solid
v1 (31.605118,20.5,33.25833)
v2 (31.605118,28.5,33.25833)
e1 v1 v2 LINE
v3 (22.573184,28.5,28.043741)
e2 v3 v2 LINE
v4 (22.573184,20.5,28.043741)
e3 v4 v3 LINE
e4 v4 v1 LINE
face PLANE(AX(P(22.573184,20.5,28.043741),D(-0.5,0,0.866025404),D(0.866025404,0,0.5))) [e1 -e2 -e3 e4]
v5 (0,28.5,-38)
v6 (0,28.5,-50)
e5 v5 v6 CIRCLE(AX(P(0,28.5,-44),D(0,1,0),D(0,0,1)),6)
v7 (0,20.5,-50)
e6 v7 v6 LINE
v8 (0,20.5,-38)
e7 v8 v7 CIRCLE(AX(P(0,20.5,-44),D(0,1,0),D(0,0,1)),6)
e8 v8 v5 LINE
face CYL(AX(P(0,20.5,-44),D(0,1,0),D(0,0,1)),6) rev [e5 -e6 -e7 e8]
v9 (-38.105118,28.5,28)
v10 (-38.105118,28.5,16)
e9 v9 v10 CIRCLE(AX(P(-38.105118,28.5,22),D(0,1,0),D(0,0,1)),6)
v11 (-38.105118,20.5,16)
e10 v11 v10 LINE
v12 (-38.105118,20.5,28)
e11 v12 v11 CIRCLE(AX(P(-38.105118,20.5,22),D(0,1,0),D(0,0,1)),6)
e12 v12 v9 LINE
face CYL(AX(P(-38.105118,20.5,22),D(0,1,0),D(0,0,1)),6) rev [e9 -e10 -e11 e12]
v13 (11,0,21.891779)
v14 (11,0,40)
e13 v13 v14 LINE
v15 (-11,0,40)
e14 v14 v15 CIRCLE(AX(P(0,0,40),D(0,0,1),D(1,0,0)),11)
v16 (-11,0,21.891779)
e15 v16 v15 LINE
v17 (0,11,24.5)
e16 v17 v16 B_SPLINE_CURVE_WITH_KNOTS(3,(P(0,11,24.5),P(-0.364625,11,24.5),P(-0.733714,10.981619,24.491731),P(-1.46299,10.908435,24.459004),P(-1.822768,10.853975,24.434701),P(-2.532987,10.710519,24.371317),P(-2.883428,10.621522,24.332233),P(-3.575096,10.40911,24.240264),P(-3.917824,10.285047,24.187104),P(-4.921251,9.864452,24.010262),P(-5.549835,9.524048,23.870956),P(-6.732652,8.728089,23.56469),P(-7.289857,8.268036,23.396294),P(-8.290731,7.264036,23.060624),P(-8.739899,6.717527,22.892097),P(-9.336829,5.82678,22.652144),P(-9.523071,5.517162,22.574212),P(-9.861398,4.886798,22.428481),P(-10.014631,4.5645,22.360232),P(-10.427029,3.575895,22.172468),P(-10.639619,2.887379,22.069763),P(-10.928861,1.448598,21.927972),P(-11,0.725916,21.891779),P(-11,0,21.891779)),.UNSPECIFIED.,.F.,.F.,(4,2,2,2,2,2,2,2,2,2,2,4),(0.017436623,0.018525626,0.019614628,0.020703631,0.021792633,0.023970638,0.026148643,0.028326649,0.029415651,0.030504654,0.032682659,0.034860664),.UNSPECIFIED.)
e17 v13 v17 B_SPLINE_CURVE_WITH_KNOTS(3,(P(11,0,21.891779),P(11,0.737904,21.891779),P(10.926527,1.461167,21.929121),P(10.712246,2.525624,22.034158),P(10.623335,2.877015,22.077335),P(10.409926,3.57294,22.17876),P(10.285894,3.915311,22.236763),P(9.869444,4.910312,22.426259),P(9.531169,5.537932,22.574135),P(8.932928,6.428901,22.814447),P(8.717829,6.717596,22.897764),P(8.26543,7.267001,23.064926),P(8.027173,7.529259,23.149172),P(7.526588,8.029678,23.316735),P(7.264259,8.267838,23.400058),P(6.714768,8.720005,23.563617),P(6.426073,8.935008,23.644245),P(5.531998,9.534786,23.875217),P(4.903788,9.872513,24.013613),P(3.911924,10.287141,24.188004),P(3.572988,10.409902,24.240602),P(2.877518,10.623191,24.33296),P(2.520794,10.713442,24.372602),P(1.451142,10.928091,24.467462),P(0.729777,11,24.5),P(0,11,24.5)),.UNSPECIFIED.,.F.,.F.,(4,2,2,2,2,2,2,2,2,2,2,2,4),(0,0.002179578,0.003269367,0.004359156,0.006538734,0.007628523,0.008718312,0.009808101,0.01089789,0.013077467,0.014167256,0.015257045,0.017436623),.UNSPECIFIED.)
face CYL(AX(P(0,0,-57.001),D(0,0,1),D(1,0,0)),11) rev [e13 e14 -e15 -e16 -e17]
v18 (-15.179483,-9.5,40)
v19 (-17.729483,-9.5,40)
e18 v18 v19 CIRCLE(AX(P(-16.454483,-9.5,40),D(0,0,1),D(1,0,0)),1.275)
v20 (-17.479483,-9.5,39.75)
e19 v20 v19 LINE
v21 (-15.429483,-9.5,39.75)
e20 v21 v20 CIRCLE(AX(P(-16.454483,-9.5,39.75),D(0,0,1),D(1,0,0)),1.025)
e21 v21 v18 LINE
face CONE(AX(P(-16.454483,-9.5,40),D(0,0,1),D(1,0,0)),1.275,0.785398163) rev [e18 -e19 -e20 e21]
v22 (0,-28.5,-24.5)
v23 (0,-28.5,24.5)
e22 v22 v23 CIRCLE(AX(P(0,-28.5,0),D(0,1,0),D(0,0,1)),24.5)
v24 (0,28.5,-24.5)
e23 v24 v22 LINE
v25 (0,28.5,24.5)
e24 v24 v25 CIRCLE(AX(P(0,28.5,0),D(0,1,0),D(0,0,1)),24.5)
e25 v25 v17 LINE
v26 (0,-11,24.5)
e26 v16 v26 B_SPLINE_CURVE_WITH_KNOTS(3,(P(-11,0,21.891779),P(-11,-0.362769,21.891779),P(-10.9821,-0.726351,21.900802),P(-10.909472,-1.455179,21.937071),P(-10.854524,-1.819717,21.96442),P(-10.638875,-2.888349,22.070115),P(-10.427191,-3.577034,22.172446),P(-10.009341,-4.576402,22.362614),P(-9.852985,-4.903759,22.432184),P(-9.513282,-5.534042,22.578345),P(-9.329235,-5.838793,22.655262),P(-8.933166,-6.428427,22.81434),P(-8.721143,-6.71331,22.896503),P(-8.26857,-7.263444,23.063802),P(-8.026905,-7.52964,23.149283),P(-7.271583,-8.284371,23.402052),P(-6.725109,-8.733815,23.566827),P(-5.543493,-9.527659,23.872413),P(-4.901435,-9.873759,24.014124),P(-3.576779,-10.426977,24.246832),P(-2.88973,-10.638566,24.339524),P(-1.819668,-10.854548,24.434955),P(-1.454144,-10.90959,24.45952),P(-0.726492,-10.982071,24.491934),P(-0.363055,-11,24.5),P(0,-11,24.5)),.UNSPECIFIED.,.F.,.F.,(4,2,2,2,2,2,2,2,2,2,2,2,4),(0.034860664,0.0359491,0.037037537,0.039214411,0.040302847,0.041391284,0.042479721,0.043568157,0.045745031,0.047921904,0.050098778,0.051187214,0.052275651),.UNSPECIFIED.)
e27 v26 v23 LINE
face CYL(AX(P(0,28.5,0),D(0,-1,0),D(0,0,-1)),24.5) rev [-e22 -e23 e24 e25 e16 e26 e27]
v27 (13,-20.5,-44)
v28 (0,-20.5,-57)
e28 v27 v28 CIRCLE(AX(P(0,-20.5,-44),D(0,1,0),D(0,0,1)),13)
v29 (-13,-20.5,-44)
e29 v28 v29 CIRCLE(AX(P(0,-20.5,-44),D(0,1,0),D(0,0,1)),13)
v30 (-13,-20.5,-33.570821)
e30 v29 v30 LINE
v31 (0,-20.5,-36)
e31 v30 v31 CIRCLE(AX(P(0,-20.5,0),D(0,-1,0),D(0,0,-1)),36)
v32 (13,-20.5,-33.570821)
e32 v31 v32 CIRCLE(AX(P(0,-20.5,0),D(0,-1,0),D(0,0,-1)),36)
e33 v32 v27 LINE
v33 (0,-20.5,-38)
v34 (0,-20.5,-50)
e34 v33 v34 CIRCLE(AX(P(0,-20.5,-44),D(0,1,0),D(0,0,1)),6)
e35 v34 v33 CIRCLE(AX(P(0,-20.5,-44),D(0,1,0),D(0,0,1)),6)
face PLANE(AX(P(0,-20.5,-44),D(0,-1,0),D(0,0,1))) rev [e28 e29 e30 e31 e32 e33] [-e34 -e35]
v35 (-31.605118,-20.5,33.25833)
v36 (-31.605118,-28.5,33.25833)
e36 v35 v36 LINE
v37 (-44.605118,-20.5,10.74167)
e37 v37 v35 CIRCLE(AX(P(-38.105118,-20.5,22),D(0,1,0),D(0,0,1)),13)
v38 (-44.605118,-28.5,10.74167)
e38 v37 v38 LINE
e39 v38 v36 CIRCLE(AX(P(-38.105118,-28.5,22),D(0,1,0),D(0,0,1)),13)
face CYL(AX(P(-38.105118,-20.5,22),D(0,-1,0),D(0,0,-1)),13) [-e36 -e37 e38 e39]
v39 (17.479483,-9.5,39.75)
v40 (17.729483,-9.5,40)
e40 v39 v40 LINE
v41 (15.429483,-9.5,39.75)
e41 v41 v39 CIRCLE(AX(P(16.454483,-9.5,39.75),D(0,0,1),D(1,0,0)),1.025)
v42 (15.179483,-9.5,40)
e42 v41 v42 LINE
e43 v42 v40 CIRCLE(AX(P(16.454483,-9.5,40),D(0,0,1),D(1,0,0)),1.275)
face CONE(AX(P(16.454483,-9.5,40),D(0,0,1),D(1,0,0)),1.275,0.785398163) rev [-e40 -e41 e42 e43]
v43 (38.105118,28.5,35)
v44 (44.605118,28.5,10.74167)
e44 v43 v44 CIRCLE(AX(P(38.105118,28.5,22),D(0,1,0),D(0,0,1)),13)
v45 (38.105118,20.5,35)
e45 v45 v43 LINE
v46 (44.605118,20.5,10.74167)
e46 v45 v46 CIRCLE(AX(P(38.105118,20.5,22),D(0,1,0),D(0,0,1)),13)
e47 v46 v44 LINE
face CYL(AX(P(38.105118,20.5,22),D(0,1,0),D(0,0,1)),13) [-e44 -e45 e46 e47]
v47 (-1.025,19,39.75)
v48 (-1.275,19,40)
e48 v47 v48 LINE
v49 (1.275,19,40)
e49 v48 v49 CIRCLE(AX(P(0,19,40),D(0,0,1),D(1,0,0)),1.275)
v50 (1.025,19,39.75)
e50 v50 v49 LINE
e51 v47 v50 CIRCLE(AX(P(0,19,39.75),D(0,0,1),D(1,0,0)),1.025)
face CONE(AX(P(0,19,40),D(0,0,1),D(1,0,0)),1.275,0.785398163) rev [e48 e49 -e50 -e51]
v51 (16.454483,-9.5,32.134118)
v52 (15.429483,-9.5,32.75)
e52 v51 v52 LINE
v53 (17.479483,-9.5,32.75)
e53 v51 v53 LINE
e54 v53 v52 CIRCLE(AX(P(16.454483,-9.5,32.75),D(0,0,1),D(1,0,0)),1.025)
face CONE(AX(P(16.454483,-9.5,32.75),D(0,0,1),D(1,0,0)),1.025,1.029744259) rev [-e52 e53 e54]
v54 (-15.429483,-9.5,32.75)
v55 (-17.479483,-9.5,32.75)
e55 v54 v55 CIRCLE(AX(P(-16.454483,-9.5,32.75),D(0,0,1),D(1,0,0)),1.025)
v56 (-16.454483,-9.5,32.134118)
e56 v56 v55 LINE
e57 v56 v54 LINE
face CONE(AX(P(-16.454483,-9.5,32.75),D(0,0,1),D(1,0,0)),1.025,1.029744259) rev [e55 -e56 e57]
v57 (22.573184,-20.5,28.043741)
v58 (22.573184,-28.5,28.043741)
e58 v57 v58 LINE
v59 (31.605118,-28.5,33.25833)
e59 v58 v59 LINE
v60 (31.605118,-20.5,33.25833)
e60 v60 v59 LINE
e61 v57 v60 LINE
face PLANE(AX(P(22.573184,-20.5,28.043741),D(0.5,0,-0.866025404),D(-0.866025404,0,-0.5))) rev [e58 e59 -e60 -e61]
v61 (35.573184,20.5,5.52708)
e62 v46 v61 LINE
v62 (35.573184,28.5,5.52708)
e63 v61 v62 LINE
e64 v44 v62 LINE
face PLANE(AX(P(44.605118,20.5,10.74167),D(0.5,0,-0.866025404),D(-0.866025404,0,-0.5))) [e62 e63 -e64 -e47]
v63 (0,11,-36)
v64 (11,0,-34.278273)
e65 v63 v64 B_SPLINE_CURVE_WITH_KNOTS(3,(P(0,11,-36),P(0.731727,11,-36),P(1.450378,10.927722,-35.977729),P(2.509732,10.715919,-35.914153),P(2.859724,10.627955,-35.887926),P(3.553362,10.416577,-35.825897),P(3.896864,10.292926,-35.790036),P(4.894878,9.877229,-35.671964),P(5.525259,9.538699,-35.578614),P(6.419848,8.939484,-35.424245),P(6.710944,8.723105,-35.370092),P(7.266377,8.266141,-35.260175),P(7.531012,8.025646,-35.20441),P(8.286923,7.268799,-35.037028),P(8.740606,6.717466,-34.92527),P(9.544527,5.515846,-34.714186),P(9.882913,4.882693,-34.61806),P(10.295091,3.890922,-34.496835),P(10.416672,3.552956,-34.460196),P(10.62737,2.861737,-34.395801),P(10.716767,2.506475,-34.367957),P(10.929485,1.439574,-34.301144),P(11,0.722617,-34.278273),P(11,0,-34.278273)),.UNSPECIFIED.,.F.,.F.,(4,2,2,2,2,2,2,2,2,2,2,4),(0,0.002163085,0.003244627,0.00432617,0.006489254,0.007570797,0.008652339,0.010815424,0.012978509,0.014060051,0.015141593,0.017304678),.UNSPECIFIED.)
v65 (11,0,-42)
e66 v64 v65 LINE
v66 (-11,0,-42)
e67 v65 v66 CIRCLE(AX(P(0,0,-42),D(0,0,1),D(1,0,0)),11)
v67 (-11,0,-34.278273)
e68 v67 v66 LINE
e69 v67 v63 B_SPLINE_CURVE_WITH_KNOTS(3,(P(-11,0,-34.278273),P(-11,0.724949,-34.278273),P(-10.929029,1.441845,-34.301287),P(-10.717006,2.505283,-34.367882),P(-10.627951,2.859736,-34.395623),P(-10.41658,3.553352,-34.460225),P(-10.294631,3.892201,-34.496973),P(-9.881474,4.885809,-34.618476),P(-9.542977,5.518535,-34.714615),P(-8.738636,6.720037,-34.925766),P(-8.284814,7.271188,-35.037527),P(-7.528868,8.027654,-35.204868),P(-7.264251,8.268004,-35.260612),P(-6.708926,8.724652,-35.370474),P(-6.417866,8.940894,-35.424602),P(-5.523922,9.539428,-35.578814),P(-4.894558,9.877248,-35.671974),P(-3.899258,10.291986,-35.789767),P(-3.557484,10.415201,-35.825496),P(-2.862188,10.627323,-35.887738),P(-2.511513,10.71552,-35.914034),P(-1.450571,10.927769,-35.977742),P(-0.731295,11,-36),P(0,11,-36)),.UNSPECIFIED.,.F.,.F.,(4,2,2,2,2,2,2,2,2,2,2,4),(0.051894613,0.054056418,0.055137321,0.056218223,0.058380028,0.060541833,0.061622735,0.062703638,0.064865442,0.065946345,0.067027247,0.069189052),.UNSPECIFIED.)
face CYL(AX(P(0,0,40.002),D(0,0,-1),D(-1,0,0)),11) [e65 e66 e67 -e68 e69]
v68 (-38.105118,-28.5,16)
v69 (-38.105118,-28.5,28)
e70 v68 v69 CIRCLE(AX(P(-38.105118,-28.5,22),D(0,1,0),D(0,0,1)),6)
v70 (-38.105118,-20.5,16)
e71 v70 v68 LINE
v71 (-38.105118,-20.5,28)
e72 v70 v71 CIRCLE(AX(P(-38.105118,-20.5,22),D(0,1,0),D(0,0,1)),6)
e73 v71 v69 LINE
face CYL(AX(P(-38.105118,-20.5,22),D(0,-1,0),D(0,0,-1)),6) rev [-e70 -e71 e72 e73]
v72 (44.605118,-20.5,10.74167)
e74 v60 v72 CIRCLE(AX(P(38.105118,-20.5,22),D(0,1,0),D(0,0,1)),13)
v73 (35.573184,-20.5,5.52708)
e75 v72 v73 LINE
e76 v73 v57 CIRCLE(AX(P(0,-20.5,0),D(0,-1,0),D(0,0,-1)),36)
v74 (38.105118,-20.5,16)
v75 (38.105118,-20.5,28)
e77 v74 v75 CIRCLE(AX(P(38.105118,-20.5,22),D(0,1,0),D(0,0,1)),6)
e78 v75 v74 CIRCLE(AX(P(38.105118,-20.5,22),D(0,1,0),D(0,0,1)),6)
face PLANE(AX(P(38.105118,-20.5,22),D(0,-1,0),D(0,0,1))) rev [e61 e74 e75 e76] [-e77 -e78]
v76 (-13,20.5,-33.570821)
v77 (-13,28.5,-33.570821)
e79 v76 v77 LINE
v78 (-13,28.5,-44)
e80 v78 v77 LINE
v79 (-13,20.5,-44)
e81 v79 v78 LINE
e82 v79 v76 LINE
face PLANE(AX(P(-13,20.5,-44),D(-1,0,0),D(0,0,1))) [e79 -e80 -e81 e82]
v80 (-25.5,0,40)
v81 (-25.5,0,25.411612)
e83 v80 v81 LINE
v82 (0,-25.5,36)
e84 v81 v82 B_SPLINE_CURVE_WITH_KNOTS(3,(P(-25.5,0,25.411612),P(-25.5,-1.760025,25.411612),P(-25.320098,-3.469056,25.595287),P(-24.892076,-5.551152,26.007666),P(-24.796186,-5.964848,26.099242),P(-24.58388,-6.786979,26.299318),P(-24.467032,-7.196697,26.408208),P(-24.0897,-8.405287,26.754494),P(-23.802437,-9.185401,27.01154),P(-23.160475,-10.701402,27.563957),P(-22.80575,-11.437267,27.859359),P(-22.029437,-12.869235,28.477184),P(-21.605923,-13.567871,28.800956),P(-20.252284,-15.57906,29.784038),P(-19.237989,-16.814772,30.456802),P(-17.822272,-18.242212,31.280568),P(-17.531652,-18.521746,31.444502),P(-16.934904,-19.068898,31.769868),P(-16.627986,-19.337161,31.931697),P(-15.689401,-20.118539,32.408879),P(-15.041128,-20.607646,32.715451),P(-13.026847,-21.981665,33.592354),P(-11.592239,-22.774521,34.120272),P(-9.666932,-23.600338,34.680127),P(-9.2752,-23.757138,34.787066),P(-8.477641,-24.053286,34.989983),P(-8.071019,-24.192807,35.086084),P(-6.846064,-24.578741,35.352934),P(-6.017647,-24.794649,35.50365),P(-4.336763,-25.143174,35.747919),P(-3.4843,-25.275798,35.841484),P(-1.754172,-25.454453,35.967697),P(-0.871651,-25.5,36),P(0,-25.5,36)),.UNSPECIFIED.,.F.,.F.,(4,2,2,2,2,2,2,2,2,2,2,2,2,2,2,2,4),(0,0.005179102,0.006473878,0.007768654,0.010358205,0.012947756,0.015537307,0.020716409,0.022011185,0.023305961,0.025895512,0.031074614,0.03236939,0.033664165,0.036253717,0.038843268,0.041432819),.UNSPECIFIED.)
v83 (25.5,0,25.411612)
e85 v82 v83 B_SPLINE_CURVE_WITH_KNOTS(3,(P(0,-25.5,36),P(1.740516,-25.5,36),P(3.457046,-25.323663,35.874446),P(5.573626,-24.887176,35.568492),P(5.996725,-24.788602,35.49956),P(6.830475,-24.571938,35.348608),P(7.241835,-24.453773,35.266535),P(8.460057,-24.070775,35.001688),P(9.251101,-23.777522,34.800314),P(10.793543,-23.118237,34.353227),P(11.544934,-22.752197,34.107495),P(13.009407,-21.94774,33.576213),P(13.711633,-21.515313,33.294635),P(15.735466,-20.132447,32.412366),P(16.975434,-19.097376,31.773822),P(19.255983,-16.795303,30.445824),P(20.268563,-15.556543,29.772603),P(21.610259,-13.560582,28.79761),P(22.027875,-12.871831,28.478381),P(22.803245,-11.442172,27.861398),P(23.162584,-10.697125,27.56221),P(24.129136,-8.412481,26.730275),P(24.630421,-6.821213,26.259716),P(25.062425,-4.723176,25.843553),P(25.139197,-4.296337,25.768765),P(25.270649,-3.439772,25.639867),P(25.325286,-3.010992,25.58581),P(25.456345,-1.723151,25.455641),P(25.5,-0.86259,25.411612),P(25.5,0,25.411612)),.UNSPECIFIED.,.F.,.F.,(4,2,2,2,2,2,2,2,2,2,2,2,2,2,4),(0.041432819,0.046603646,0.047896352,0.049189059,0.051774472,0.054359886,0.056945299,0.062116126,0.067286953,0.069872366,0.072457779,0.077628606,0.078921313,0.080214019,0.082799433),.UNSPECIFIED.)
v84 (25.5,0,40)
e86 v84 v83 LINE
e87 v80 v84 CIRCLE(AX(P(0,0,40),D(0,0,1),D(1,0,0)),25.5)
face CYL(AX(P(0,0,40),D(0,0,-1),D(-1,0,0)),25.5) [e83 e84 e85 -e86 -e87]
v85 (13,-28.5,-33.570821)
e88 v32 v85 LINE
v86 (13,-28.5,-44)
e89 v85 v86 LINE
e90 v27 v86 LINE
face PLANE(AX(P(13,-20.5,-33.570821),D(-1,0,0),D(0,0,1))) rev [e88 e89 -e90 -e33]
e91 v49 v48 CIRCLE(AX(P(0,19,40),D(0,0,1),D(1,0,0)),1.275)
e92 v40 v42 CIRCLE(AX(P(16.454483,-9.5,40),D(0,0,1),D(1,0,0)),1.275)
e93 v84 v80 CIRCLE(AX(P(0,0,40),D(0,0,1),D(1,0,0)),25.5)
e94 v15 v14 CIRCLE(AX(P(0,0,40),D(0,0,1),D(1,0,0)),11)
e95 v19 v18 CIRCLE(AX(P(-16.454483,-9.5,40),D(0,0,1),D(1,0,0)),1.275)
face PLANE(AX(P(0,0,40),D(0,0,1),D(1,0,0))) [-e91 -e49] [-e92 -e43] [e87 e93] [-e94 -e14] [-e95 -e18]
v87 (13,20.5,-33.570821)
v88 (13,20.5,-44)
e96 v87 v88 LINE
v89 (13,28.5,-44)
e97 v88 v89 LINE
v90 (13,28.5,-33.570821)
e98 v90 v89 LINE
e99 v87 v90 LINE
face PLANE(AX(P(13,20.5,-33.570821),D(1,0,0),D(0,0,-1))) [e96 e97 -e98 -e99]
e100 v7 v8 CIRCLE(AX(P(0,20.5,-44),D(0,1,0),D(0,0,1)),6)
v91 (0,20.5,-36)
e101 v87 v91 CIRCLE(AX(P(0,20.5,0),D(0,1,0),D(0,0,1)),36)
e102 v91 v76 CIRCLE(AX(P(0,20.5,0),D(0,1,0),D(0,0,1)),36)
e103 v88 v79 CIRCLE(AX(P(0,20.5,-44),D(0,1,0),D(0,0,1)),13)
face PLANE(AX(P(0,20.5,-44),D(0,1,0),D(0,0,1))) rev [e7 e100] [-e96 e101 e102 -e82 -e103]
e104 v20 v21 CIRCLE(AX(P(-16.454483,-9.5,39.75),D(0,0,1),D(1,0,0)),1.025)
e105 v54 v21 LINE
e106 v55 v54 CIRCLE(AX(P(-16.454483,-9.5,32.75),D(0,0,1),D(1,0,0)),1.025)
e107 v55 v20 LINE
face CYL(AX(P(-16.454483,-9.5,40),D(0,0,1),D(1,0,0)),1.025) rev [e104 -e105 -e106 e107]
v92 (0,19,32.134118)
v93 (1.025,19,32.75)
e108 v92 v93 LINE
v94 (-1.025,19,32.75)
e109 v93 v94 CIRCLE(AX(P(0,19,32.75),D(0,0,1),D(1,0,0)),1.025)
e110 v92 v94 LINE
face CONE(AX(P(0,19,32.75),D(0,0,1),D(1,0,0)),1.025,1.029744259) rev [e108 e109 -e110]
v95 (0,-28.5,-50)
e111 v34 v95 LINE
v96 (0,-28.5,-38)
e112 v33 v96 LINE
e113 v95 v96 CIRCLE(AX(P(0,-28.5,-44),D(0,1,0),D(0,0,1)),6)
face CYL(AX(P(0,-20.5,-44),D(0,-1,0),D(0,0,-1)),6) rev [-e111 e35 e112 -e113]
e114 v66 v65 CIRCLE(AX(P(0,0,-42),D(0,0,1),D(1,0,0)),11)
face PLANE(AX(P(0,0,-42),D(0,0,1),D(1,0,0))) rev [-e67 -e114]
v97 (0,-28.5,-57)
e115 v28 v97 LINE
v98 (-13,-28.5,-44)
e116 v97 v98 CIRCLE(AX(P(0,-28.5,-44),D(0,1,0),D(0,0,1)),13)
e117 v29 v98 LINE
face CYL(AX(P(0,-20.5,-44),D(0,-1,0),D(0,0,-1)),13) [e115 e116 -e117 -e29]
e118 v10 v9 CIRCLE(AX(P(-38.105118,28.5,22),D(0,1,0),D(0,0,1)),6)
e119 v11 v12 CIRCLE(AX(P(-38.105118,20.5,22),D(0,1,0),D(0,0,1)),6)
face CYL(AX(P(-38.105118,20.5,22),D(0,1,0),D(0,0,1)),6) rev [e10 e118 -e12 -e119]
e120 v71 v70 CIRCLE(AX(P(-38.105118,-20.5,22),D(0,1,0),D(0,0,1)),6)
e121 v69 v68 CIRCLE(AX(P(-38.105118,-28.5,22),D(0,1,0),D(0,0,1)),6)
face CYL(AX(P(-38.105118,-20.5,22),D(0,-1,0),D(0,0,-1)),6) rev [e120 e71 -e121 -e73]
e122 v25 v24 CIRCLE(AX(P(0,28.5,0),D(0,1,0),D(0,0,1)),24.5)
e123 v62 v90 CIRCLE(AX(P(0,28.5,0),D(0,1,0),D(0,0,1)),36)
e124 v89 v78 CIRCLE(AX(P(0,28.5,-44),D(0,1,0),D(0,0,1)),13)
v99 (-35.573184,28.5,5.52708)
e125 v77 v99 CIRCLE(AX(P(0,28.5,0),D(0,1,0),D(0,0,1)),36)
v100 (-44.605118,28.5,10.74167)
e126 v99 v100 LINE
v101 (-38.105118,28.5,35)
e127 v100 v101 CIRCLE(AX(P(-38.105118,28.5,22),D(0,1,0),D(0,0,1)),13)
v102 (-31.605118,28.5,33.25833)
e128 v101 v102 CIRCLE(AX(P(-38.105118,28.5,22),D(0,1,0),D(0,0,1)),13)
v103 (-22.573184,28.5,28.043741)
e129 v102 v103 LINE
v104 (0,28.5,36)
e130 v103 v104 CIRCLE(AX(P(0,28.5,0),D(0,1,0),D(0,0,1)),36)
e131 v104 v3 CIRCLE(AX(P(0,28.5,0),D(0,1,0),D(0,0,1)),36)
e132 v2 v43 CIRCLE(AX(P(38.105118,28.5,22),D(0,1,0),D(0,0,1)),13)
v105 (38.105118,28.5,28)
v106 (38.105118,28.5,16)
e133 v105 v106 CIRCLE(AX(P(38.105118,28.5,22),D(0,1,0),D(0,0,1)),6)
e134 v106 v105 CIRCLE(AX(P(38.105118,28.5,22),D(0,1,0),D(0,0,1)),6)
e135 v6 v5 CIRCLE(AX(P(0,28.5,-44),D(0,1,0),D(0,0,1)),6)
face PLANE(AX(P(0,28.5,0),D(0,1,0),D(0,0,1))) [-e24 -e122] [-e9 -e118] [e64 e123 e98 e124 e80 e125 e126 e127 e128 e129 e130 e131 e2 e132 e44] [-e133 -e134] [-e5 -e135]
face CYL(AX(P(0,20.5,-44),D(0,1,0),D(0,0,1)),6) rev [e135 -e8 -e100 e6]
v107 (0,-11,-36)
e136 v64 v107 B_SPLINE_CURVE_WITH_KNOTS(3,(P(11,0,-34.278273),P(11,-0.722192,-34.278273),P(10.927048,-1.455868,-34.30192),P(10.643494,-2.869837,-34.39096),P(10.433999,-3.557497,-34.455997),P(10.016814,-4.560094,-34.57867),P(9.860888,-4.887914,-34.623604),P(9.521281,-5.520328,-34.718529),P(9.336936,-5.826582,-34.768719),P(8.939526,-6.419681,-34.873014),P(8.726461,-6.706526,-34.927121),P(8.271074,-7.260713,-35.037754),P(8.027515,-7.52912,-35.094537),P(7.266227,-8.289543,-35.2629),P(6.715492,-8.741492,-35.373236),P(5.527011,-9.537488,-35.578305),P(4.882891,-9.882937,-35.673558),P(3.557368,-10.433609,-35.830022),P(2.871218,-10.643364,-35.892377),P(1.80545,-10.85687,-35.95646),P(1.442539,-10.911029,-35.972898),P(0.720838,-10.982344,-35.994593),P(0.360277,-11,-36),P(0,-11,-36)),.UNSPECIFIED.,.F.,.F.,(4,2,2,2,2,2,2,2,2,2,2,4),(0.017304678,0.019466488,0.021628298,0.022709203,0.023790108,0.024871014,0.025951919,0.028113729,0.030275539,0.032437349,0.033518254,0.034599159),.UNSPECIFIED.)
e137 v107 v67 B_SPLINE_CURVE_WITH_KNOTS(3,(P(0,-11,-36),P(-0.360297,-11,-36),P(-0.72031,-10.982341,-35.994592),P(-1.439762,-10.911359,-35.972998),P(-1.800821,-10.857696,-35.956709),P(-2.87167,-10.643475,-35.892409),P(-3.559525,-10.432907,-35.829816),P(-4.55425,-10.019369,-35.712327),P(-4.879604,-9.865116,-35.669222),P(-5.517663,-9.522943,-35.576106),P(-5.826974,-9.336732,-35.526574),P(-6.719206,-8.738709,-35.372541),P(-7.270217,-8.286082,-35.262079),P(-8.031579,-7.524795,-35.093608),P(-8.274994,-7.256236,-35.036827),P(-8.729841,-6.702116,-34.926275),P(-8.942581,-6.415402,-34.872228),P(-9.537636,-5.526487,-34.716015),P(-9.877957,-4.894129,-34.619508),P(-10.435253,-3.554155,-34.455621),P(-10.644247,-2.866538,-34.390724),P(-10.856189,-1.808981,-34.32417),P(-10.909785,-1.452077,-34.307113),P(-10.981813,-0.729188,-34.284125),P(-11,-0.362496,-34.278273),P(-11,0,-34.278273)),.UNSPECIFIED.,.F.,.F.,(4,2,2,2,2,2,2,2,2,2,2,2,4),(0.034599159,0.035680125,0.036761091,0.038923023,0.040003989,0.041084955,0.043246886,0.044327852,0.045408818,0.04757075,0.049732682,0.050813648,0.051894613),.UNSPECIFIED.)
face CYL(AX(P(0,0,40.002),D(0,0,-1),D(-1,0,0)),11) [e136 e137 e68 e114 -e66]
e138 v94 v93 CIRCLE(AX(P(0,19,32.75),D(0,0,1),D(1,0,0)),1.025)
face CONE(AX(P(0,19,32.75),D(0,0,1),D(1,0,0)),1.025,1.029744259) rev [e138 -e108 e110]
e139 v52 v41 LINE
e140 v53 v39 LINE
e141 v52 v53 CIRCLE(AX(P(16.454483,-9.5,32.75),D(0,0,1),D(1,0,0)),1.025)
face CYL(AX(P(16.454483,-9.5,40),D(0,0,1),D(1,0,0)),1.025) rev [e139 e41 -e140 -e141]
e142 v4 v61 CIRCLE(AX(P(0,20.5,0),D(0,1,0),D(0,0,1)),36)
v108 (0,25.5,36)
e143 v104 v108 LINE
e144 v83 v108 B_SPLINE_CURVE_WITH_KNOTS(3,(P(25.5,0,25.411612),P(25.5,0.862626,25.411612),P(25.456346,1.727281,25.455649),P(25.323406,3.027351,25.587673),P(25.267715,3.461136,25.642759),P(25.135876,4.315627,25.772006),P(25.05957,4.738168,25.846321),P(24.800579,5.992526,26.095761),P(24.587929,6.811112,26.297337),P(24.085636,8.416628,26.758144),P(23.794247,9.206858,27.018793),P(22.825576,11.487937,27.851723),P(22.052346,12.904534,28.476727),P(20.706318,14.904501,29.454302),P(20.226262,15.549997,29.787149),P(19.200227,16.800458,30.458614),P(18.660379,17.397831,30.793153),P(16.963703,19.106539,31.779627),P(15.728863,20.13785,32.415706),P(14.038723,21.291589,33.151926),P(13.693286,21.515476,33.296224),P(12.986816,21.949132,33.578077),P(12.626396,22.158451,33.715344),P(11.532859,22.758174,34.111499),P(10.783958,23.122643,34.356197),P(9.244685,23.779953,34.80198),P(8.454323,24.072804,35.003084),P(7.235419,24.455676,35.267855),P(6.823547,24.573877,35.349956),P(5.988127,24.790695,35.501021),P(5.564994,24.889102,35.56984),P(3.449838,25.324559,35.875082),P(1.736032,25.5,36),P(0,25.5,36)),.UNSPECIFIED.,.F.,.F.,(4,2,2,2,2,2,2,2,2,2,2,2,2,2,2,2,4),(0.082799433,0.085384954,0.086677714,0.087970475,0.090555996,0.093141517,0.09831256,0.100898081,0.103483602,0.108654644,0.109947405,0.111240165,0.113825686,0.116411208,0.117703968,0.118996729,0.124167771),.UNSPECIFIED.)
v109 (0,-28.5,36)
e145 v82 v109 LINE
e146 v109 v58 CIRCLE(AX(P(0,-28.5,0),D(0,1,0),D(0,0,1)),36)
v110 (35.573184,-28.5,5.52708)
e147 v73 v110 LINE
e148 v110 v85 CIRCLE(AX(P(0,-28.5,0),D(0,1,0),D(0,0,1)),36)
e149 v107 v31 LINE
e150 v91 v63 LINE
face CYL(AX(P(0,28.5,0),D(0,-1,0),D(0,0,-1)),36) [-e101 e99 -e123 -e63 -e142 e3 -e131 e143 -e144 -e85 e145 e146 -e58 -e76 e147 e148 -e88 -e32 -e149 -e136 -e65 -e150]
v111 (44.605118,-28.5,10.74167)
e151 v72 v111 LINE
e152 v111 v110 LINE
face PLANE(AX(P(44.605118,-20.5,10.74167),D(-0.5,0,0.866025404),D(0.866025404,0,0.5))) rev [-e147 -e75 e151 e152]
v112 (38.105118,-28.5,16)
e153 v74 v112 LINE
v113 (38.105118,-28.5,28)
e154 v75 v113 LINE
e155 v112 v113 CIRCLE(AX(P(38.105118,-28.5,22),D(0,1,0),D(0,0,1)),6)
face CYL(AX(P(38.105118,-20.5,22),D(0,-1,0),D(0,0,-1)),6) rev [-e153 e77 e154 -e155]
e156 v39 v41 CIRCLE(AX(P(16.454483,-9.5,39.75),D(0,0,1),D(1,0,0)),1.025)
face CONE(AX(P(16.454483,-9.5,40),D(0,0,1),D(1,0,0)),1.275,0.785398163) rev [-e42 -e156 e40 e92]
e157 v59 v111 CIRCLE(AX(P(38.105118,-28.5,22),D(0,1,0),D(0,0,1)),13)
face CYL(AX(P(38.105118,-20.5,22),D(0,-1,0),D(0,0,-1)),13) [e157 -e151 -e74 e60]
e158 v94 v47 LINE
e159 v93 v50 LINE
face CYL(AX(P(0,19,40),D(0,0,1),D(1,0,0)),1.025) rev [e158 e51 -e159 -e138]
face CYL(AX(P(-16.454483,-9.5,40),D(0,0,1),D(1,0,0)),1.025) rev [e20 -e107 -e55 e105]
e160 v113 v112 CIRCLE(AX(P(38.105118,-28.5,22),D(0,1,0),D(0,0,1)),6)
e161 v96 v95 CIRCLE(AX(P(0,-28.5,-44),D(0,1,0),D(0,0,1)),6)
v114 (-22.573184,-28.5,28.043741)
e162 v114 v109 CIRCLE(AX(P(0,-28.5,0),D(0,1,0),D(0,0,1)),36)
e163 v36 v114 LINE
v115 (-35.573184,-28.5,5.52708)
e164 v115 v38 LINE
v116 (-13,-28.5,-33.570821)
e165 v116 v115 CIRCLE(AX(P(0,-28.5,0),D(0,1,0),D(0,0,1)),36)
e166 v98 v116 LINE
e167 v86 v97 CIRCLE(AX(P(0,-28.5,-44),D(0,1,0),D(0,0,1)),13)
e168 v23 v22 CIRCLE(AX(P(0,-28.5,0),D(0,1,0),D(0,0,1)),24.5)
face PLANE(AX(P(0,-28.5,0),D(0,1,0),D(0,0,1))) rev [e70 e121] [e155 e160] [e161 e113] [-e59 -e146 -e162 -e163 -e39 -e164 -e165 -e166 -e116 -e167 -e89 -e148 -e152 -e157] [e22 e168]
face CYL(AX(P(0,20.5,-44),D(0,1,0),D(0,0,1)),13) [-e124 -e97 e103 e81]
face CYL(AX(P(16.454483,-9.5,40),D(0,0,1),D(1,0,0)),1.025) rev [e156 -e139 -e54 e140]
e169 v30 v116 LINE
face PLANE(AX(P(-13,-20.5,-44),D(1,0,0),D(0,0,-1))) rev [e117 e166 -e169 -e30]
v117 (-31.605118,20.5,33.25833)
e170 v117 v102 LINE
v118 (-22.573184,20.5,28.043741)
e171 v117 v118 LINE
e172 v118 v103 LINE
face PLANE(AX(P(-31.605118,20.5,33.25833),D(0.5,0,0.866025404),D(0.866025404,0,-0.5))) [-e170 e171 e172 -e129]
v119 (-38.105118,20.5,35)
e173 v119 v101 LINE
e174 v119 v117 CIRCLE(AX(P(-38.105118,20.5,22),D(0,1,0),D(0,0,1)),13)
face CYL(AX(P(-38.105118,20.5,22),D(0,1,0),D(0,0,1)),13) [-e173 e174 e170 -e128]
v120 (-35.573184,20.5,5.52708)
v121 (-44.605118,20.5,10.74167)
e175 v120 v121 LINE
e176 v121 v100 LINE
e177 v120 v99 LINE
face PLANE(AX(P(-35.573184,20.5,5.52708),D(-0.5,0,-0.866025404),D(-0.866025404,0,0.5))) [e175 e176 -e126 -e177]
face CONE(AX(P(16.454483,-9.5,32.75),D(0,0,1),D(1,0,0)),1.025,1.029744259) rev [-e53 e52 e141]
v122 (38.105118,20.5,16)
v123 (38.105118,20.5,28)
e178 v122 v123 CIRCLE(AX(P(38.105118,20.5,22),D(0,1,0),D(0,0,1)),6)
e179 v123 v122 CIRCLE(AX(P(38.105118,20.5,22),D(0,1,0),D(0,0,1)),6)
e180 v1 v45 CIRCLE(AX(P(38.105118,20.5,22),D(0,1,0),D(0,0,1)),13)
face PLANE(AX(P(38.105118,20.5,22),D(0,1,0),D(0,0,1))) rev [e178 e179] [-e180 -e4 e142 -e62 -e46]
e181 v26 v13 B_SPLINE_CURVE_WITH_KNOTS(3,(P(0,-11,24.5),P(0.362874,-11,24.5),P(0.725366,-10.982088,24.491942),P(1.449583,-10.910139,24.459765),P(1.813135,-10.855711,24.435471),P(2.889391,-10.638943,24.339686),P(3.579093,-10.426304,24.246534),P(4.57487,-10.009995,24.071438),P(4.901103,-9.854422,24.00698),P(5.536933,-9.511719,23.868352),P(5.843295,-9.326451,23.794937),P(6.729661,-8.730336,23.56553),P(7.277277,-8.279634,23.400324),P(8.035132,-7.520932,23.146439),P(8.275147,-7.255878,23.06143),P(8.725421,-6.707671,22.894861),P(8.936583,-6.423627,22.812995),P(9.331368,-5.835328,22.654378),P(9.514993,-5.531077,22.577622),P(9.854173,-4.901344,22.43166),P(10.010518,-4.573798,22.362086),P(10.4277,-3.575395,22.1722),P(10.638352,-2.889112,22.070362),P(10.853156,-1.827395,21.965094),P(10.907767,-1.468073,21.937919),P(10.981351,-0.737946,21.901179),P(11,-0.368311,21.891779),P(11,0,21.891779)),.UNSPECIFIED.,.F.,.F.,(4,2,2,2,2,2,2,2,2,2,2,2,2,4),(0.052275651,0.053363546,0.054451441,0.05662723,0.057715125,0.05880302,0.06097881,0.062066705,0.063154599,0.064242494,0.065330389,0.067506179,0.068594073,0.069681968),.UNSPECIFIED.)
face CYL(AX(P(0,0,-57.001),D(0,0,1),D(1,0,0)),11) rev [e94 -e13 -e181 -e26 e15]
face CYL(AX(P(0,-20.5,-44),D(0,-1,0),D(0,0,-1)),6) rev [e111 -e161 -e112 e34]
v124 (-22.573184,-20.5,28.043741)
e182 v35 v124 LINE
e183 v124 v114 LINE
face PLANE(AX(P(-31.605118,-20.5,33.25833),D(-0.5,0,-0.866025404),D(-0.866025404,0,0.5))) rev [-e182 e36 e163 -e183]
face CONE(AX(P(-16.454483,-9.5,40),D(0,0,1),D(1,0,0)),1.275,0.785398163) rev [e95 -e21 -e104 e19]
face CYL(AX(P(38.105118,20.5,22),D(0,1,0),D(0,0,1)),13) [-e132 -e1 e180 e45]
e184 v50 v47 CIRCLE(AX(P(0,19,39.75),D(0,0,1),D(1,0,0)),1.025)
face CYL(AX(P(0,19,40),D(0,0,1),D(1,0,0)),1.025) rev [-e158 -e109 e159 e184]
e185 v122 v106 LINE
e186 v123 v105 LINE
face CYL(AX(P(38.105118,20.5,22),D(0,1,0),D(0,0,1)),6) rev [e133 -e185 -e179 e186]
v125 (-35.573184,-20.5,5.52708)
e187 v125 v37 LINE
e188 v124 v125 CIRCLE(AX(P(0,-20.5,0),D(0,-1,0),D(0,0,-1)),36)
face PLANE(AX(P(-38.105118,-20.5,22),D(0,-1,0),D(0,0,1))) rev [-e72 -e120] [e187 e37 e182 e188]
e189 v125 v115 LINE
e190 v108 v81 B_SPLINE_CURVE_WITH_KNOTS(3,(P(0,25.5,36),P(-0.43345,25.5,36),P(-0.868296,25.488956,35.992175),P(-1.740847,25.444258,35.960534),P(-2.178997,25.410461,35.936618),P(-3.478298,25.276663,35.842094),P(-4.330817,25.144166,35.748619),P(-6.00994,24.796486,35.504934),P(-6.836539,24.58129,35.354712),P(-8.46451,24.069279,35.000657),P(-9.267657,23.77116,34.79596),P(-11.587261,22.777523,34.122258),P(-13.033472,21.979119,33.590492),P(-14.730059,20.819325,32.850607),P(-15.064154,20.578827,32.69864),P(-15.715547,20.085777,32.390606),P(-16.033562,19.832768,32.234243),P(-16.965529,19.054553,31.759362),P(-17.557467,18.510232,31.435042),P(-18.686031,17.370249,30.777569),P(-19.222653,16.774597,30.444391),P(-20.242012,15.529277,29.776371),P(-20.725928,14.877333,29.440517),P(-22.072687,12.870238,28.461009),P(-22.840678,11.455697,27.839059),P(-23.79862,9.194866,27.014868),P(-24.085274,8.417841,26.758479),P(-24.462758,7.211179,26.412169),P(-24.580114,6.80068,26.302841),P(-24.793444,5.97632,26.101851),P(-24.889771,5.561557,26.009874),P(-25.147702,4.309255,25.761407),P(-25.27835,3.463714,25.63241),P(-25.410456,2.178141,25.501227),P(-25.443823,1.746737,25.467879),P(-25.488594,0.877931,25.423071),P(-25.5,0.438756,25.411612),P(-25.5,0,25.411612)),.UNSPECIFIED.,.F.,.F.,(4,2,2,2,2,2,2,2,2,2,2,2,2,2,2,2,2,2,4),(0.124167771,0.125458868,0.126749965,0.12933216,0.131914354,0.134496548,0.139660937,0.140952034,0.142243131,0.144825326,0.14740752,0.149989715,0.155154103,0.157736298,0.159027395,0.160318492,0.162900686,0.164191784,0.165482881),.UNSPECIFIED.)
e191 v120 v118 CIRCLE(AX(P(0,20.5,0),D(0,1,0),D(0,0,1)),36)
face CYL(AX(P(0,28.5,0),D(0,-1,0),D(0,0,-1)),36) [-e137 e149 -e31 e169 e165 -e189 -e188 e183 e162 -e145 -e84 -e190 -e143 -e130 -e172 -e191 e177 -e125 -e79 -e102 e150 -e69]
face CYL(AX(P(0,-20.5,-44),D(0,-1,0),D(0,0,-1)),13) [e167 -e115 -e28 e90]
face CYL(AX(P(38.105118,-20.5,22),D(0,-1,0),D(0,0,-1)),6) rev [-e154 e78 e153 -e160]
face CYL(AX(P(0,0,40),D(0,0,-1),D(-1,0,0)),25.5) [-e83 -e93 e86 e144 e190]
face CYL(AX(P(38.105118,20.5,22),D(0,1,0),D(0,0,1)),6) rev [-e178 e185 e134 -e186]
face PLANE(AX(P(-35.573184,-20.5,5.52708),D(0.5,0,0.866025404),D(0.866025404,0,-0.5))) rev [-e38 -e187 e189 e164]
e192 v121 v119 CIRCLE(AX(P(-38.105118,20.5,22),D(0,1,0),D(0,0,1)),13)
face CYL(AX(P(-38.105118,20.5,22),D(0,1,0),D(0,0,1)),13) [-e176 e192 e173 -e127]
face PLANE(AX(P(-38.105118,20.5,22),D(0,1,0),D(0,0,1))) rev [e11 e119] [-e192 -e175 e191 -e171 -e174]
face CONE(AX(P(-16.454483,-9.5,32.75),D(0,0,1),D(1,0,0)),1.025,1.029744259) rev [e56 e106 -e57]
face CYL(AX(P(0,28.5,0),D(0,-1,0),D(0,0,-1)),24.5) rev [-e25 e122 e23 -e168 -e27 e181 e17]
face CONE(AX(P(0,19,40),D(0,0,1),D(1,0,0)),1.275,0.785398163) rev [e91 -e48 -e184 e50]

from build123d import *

# Parameters (mm, degrees)
MAIN_BODY_PROFILE_SKETCH_R             = 36
MAIN_BODY_PROFILE_SKETCH_R_2           = 24.5
MAIN_BODY_DEPTH                        = 28.5
MOUNTING_LUGS_SKETCH_R                 = 6
TOP_MOUNTING_LUGS_3X_DEPTH             = 8
SIDE_PORT_BOSS_SKETCH_51_R             = 25.5
SIDE_PORT_BOSS_51_DEPTH                = 40
PORT_TAPPED_HOLES_3XM2_5_PATTERN_COUNT = 3
MAIN_BORE_SKETCH_R                     = 24.5
MAIN_BORE_DEPTH                        = 96.444921674
SIDE_PORT_BORE_22_REACH                = 115.283
SIDE_PORT_BORE_22_END_RADIUS           = 24.5
SIDE_PORT_BORE_SKETCH_22_R             = 11
INTERNAL_BOSS_REACH                    = 102.737
INTERNAL_BOSS_END_RADIUS               = 36
INTERNAL_BOSS_SKETCH_R                 = 11


with BuildPart() as part:
    # Main Body Profile Sketch → Main Body (new, symmetric)
    with BuildSketch(Plane(origin=(0, 0, 0), x_dir=(1, 0, 0), z_dir=(0, 1, 0))):
        with Locations(Location((0, 0, 0), (0, 0, 90))):
            Circle(MAIN_BODY_PROFILE_SKETCH_R)
        with Locations(Location((0, 0, 0), (0, 0, 90))):
            Circle(MAIN_BODY_PROFILE_SKETCH_R_2, mode=Mode.SUBTRACT)
    extrude(amount=MAIN_BODY_DEPTH, both=True)

    # Mounting Lugs Sketch → Top Mounting Lugs 3x (add)
    # profile 1 of 3: a face of its own
    with BuildSketch(Plane(origin=(0, 28.5, 0), x_dir=(1, 0, 0), z_dir=(0, 1, 0))):
        with BuildLine():
            Line((-13, 44), (-13, 33.570820663))
            Line((-13, 33.570820663), (13, 33.570820663))
            Line((13, 33.570820663), (13, 44))
            ThreePointArc((13, 44), (0, 57), (-13, 44))
        make_face()
        with Locations(Location((0, 44, 0), (0, 0, 270))):
            Circle(MOUNTING_LUGS_SKETCH_R, mode=Mode.SUBTRACT)
    # profile 2 of 3: a face of its own
    with BuildSketch(Plane(origin=(0, 28.5, 0), x_dir=(1, 0, 0), z_dir=(0, 1, 0))):
        with BuildLine():
            Line((44.605117767, -10.741669751), (35.57318352, -5.527080082))
            Line((35.57318352, -5.527080082), (22.57318352, -28.043740581))
            Line((22.57318352, -28.043740581), (31.605117767, -33.258330249))
            ThreePointArc((31.605117767, -33.258330249), (49.363448016, -28.5), (44.605117767, -10.741669751))
        make_face()
        with Locations(Location((38.105117767, -22, 0), (0, 0, 270))):
            Circle(MOUNTING_LUGS_SKETCH_R, mode=Mode.SUBTRACT)
    # profile 3 of 3: a face of its own
    with BuildSketch(Plane(origin=(0, 28.5, 0), x_dir=(1, 0, 0), z_dir=(0, 1, 0))):
        with BuildLine():
            Line((-31.605117767, -33.258330249), (-22.57318352, -28.043740581))
            Line((-22.57318352, -28.043740581), (-35.57318352, -5.527080082))
            Line((-35.57318352, -5.527080082), (-44.605117767, -10.741669751))
            ThreePointArc((-44.605117767, -10.741669751), (-49.363448016, -28.5), (-31.605117767, -33.258330249))
        make_face()
        with Locations(Location((-38.105117767, -22, 0), (0, 0, 270))):
            Circle(MOUNTING_LUGS_SKETCH_R, mode=Mode.SUBTRACT)
    top_mounting_lugs_3x = extrude(amount=-TOP_MOUNTING_LUGS_3X_DEPTH)

    # Bottom Mounting Lugs Mirror: Top Mounting Lugs 3x across plane
    add(top_mounting_lugs_3x.mirror(Plane.ZX))

    # Side Port Boss Sketch Ø51 → Side Port Boss Ø51 (add)
    with BuildSketch(Plane.XY):
        with Locations(Location((0, 0, 0), (0, 0, 180))):
            Circle(SIDE_PORT_BOSS_SKETCH_51_R)
    extrude(amount=SIDE_PORT_BOSS_51_DEPTH)

    # Sketch5 → Port Tapped Hole M2.5 (revolve, cut)
    with BuildSketch(Plane(origin=(0, 19, 40), x_dir=(0, -1, 0), z_dir=(1, 0, 0))):
        Polygon((0, 0), (0, 7.865882135), (1.025, 7.25), (1.025, 0.25), (1.275, 0), align=None)
    port_tapped_hole_m2_5 = revolve(axis=Axis((0, 19, 46.35), (0, 0, -1)), mode=Mode.SUBTRACT)

    # Port Tapped Holes 3xM2.5 Pattern: Port Tapped Hole M2.5 ×3 about axis
    port_tapped_holes_3xm2_5_pattern_axis = Axis((0, 0, 0), (0, 0, 1))
    for i in range(1, PORT_TAPPED_HOLES_3XM2_5_PATTERN_COUNT):
        add(port_tapped_hole_m2_5.rotate(port_tapped_holes_3xm2_5_pattern_axis, i * 360 / PORT_TAPPED_HOLES_3XM2_5_PATTERN_COUNT), mode=Mode.SUBTRACT)

    # Main Bore Sketch → Main Bore (cut, through all)
    with BuildSketch(Plane(origin=(0, 28.5, 0), x_dir=(1, 0, 0), z_dir=(0, 1, 0))):
        with Locations(Location((0, 0, 0), (0, 0, 90))):
            Circle(MAIN_BORE_SKETCH_R)
    extrude(amount=-MAIN_BORE_DEPTH, mode=Mode.SUBTRACT)

    # Side Port Bore Ø22: up to this cylinder (the profile starts outside it)
    side_port_bore_22_end = Plane(origin=(0, 0, 0), z_dir=(0, -1, 0)) * Cylinder(SIDE_PORT_BORE_22_END_RADIUS, 280.566, mode=Mode.PRIVATE)
    # Side Port Bore Sketch Ø22 → Side Port Bore Ø22 (cut, up to the surface)
    with BuildSketch(Plane.XY.offset(40), mode=Mode.PRIVATE) as side_port_bore_22_sk1:
        Circle(SIDE_PORT_BORE_SKETCH_22_R)
    side_port_bore_22_tool1 = extrude(side_port_bore_22_sk1.sketch, amount=-SIDE_PORT_BORE_22_REACH, mode=Mode.PRIVATE) - side_port_bore_22_end
    add(side_port_bore_22_tool1.solids().sort_by_distance((0, 0, 40))[0], mode=Mode.SUBTRACT)

    # Internal Boss: up to this cylinder (the profile starts outside it)
    internal_boss_end = Plane(origin=(0, 0, 0), z_dir=(0, -1, 0)) * Cylinder(INTERNAL_BOSS_END_RADIUS, 278.474, mode=Mode.PRIVATE)
    # Internal Boss Sketch → Internal Boss (add, up to the surface)
    with BuildSketch(Plane.XY.offset(-42), mode=Mode.PRIVATE) as internal_boss_sk1:
        Circle(INTERNAL_BOSS_SKETCH_R)
    internal_boss_tool1 = extrude(internal_boss_sk1.sketch, amount=INTERNAL_BOSS_REACH, mode=Mode.PRIVATE) - internal_boss_end
    add(internal_boss_tool1.solids().sort_by_distance((0, 0, -42))[0])


solid = part.part
